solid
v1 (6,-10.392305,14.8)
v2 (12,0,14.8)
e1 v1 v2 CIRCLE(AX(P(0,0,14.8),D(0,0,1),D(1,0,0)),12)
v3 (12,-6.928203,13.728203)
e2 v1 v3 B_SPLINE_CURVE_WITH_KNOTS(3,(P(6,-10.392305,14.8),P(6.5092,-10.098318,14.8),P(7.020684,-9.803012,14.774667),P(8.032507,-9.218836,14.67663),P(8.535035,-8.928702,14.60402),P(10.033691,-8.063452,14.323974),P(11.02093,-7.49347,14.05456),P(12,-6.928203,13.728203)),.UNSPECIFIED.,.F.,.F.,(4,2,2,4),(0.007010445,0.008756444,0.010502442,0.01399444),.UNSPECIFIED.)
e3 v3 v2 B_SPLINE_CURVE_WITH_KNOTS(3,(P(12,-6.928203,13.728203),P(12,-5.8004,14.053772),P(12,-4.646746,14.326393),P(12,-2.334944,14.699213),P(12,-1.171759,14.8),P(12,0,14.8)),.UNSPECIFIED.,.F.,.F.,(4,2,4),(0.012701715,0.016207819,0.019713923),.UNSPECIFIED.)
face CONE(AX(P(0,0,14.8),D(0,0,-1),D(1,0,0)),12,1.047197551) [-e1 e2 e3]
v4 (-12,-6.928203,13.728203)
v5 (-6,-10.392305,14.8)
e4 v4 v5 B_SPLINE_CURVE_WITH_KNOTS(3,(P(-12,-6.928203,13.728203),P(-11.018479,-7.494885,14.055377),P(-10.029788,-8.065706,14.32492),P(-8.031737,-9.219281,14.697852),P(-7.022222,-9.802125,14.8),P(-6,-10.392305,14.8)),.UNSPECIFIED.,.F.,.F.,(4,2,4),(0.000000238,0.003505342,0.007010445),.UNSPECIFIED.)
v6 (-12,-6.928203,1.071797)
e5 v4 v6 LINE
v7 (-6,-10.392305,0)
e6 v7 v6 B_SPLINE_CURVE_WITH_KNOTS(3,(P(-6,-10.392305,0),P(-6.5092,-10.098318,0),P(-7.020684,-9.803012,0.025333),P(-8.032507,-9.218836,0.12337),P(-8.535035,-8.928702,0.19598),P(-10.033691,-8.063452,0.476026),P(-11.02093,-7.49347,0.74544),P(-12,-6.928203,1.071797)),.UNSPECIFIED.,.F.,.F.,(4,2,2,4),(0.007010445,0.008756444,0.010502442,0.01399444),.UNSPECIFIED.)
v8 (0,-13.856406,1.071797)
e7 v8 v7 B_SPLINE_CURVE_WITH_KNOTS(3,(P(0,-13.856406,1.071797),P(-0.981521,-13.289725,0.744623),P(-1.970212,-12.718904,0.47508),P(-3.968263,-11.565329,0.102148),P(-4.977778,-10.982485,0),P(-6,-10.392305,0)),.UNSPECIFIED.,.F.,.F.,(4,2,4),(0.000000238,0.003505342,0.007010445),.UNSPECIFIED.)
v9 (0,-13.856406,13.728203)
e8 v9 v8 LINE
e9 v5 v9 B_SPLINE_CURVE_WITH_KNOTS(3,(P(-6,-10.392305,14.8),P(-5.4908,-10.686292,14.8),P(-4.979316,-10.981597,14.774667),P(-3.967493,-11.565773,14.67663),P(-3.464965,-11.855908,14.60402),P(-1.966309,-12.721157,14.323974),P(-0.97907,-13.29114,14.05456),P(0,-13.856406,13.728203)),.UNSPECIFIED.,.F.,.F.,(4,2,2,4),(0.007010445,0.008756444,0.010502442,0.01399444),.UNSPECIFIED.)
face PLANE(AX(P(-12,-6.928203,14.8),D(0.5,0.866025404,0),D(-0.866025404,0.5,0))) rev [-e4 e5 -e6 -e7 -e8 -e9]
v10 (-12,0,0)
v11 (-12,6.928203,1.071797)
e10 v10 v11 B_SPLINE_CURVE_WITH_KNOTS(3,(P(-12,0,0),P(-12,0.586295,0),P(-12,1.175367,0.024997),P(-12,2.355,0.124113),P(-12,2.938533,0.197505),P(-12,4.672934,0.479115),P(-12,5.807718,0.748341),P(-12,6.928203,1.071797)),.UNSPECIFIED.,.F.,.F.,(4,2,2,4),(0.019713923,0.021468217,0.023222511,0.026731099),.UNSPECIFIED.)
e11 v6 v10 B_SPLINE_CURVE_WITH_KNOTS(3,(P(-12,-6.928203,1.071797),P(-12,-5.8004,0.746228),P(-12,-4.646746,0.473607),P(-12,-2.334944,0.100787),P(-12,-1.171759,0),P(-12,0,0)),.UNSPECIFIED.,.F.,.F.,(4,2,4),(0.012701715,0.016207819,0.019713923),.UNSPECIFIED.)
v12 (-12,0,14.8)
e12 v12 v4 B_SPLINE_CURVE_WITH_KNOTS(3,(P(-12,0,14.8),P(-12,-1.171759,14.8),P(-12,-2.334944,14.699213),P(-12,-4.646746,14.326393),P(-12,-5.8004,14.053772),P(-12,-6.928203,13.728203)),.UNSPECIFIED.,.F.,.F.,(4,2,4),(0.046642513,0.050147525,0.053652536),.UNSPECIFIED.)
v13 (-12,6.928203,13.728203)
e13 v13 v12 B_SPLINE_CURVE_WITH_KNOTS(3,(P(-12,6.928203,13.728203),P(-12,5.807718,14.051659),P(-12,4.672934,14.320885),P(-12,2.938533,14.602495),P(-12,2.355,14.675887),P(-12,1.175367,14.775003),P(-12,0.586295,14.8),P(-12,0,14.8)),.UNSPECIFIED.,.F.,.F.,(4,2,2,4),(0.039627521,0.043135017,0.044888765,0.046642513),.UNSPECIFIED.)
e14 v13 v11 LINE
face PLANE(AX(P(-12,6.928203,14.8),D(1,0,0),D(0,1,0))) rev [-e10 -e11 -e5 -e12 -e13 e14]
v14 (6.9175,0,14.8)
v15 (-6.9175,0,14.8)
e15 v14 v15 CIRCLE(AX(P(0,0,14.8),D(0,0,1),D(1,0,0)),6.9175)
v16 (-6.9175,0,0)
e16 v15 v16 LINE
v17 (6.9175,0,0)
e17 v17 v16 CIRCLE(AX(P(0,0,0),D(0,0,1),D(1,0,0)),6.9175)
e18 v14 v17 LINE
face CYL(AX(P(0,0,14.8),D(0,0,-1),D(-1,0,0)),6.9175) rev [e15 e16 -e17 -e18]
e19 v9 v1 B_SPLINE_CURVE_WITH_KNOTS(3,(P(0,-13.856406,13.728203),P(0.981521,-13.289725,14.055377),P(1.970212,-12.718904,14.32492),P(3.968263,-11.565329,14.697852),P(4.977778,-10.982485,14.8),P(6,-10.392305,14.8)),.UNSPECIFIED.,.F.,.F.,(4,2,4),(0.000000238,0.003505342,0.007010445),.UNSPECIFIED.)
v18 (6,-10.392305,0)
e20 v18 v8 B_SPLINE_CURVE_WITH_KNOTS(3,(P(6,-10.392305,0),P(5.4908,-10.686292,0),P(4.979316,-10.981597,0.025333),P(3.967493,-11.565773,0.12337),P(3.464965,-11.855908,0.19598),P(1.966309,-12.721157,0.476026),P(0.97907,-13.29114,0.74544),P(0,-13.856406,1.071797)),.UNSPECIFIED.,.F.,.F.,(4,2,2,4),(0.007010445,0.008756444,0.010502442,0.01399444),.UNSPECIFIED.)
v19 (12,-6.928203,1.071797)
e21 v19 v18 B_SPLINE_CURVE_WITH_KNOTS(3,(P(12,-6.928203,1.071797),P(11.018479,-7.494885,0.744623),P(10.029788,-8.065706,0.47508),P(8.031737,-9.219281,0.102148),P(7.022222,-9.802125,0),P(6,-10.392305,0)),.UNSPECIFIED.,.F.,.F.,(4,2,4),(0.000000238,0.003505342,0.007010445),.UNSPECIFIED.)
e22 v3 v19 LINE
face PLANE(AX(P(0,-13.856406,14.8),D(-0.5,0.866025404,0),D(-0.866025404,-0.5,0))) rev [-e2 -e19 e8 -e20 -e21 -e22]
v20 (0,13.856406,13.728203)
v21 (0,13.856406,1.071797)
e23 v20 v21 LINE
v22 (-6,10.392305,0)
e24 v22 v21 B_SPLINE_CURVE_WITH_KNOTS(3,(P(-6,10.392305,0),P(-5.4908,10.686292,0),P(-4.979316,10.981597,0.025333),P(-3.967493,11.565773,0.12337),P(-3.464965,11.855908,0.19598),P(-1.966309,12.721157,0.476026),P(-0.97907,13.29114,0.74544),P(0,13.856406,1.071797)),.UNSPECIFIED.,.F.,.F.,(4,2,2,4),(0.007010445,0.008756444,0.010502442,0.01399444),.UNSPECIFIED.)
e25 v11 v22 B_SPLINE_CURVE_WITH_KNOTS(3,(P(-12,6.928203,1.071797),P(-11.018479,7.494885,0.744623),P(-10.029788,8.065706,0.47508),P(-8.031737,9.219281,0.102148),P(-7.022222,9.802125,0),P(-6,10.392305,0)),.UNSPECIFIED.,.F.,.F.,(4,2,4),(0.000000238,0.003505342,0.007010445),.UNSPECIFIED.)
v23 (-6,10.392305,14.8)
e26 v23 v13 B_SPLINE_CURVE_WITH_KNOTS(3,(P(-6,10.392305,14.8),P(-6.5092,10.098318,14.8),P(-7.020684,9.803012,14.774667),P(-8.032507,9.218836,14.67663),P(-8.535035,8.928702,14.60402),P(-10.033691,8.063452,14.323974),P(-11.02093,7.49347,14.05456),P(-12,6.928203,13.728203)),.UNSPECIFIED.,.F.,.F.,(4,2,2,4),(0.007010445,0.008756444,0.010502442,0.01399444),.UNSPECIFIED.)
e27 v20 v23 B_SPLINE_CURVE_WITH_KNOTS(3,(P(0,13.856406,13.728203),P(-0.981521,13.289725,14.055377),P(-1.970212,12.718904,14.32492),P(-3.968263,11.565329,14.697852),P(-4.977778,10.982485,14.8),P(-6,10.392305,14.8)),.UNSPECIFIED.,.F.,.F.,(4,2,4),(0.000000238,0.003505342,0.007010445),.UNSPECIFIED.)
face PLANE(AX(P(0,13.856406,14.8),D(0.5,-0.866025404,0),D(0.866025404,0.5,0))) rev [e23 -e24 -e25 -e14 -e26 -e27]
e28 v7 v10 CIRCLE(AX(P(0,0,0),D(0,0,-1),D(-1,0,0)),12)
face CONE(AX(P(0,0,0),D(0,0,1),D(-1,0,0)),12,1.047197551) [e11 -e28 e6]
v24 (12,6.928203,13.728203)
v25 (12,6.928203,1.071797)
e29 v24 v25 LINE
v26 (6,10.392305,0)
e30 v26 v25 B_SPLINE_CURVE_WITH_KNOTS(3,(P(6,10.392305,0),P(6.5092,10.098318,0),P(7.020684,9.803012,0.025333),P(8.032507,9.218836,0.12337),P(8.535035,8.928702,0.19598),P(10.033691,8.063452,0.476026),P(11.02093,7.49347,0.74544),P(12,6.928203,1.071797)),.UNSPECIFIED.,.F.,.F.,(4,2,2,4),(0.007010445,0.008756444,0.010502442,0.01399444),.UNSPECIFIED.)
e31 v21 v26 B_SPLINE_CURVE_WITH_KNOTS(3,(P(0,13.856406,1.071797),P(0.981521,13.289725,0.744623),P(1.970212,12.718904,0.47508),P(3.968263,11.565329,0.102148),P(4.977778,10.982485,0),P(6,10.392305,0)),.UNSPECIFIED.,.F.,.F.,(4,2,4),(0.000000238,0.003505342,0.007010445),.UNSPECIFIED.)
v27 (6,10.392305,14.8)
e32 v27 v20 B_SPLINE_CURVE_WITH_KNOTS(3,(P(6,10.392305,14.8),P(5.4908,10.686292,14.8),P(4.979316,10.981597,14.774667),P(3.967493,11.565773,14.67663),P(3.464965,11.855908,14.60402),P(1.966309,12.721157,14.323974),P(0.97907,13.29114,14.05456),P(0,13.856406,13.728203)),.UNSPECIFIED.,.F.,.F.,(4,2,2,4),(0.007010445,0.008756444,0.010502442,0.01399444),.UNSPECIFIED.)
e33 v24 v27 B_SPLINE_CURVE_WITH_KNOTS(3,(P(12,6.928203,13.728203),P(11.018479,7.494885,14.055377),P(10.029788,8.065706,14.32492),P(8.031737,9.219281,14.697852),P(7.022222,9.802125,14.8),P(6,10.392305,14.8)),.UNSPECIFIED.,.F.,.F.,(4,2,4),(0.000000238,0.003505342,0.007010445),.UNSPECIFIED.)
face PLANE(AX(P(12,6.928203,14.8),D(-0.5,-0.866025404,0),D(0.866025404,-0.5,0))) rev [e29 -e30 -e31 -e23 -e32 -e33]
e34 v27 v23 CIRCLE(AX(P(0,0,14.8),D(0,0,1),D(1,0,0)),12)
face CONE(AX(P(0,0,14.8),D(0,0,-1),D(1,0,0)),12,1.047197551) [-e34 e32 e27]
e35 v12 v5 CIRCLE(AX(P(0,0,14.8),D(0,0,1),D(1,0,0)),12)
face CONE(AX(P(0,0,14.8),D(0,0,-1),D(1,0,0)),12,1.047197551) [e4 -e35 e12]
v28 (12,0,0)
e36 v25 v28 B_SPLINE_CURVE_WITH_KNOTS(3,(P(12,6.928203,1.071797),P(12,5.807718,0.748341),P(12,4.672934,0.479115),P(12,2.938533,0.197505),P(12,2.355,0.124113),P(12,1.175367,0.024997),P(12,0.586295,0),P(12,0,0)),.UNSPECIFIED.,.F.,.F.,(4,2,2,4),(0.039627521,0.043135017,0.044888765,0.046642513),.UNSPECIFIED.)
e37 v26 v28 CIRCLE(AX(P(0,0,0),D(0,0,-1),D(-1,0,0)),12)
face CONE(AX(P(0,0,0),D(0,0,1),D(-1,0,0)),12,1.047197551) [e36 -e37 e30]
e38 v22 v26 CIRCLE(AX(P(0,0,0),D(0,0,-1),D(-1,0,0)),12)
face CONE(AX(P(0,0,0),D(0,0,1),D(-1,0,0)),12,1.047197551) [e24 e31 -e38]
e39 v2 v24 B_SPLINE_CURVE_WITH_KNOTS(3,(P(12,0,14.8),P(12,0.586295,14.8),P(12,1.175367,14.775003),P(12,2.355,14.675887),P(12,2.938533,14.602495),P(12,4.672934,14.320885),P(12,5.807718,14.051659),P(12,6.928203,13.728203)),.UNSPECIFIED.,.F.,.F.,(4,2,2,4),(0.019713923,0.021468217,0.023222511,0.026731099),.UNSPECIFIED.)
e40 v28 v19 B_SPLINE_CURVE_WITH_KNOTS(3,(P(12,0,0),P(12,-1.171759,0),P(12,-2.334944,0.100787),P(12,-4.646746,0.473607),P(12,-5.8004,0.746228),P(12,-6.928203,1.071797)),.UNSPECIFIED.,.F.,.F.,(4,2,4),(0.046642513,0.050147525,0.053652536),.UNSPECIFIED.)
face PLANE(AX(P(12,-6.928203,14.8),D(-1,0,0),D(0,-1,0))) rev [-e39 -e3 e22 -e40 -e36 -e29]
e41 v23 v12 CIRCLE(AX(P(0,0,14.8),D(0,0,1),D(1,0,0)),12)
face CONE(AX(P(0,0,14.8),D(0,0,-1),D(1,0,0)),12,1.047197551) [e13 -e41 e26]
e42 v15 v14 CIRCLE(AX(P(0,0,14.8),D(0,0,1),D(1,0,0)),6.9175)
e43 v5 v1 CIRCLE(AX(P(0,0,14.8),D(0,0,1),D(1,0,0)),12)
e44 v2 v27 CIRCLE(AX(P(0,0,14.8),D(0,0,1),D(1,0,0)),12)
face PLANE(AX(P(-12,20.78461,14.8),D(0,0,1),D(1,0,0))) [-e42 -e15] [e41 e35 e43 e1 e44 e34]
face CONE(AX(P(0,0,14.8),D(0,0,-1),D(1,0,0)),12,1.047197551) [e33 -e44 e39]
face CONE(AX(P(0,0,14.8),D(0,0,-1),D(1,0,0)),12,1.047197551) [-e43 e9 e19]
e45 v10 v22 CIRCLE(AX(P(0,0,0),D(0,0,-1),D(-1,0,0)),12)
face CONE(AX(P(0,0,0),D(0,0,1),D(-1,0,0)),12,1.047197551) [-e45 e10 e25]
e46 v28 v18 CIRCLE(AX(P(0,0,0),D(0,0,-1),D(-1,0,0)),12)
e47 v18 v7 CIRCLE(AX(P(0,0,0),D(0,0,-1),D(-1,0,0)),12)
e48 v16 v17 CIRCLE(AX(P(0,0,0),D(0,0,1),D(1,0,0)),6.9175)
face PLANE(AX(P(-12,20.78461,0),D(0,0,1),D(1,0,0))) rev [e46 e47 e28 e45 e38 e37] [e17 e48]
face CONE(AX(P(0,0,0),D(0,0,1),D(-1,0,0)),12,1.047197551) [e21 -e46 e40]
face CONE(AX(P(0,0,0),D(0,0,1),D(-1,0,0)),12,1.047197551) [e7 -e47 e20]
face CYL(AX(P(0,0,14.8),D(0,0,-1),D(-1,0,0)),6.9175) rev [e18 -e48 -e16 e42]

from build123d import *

# Parameters (mm, degrees)
SKETCH_1_R          = 6.9175
EXTRUDE_597_DEPTH   = 14.8
SKETCH_2_OUTSIDE_W  = 118.982
SKETCH_2_OUTSIDE_H  = 122.694
SKETCH_2_OUTSIDE_R  = 12
CUT_EXTRUDE_1_DEPTH = 24.559286916
CUT_EXTRUDE_1_DRAFT = -60
SKETCH_3_OUTSIDE_W  = 118.982
SKETCH_3_OUTSIDE_H  = 122.694
SKETCH_3_OUTSIDE_R  = 12
CUT_EXTRUDE_2_DEPTH = 24.559286916
CUT_EXTRUDE_2_DRAFT = -60


with BuildPart() as part:
    # 草图1 → Extrude 597 (new body)
    with BuildSketch(Plane.XY):
        Polygon((0, 13.856406461), (-12, 6.92820323), (-12, -6.92820323), (0, -13.856406461), (12, -6.92820323), (12, 6.92820323), align=None)
        Circle(SKETCH_1_R, mode=Mode.SUBTRACT)
    extrude(amount=EXTRUDE_597_DEPTH)


with BuildPart() as cut_extrude_1_tool:
    # 草图2 outside → 切除-拉伸1 (with draft: the straight prism first)
    with BuildSketch(Plane(origin=(0, 0, 0), x_dir=(-1, 0, 0), z_dir=(0, 0, -1))):
        Rectangle(SKETCH_2_OUTSIDE_W, SKETCH_2_OUTSIDE_H)
        Circle(SKETCH_2_OUTSIDE_R, mode=Mode.SUBTRACT)
    extrude(amount=-CUT_EXTRUDE_1_DEPTH)
    # 切除-拉伸1: the draft: its side faces are tilted about the plane it starts from
    cut_extrude_1_sides = [cut_extrude_1_tool.faces().sort_by_distance(p)[0] for p in [
        (0, -61.347, 12.279643458),
        (-59.491, 0, 12.279643458),
        (0, 61.347, 12.279643458),
        (59.491, 0, 12.279643458),
        (12, 0, 12.279643458),
    ]]
    draft(cut_extrude_1_sides, Plane(origin=(0, 0, 0), x_dir=(-1, 0, 0), z_dir=(0, 0, -1)), CUT_EXTRUDE_1_DRAFT)


with BuildPart() as part_1:
    add(part.part)

    # 切除-拉伸1: cut by cut_extrude_1_tool
    add(cut_extrude_1_tool.part, mode=Mode.SUBTRACT)


with BuildPart() as cut_extrude_2_tool:
    # 草图3 outside → 切除-拉伸2 (with draft: the straight prism first)
    with BuildSketch(Plane.XY.offset(14.8)):
        Rectangle(SKETCH_3_OUTSIDE_W, SKETCH_3_OUTSIDE_H)
        Circle(SKETCH_3_OUTSIDE_R, mode=Mode.SUBTRACT)
    extrude(amount=-CUT_EXTRUDE_2_DEPTH)
    # 切除-拉伸2: the draft: its side faces are tilted about the plane it starts from
    cut_extrude_2_sides = [cut_extrude_2_tool.faces().sort_by_distance(p)[0] for p in [
        (0, -61.347, 2.520356542),
        (59.491, 0, 2.520356542),
        (0, 61.347, 2.520356542),
        (-59.491, 0, 2.520356542),
        (-12, 0, 2.520356542),
    ]]
    draft(cut_extrude_2_sides, Plane.XY.offset(14.8), CUT_EXTRUDE_2_DRAFT)


with BuildPart() as part_2:
    add(part_1.part)

    # 切除-拉伸2: cut by cut_extrude_2_tool
    add(cut_extrude_2_tool.part, mode=Mode.SUBTRACT)


solid = part_2.part
